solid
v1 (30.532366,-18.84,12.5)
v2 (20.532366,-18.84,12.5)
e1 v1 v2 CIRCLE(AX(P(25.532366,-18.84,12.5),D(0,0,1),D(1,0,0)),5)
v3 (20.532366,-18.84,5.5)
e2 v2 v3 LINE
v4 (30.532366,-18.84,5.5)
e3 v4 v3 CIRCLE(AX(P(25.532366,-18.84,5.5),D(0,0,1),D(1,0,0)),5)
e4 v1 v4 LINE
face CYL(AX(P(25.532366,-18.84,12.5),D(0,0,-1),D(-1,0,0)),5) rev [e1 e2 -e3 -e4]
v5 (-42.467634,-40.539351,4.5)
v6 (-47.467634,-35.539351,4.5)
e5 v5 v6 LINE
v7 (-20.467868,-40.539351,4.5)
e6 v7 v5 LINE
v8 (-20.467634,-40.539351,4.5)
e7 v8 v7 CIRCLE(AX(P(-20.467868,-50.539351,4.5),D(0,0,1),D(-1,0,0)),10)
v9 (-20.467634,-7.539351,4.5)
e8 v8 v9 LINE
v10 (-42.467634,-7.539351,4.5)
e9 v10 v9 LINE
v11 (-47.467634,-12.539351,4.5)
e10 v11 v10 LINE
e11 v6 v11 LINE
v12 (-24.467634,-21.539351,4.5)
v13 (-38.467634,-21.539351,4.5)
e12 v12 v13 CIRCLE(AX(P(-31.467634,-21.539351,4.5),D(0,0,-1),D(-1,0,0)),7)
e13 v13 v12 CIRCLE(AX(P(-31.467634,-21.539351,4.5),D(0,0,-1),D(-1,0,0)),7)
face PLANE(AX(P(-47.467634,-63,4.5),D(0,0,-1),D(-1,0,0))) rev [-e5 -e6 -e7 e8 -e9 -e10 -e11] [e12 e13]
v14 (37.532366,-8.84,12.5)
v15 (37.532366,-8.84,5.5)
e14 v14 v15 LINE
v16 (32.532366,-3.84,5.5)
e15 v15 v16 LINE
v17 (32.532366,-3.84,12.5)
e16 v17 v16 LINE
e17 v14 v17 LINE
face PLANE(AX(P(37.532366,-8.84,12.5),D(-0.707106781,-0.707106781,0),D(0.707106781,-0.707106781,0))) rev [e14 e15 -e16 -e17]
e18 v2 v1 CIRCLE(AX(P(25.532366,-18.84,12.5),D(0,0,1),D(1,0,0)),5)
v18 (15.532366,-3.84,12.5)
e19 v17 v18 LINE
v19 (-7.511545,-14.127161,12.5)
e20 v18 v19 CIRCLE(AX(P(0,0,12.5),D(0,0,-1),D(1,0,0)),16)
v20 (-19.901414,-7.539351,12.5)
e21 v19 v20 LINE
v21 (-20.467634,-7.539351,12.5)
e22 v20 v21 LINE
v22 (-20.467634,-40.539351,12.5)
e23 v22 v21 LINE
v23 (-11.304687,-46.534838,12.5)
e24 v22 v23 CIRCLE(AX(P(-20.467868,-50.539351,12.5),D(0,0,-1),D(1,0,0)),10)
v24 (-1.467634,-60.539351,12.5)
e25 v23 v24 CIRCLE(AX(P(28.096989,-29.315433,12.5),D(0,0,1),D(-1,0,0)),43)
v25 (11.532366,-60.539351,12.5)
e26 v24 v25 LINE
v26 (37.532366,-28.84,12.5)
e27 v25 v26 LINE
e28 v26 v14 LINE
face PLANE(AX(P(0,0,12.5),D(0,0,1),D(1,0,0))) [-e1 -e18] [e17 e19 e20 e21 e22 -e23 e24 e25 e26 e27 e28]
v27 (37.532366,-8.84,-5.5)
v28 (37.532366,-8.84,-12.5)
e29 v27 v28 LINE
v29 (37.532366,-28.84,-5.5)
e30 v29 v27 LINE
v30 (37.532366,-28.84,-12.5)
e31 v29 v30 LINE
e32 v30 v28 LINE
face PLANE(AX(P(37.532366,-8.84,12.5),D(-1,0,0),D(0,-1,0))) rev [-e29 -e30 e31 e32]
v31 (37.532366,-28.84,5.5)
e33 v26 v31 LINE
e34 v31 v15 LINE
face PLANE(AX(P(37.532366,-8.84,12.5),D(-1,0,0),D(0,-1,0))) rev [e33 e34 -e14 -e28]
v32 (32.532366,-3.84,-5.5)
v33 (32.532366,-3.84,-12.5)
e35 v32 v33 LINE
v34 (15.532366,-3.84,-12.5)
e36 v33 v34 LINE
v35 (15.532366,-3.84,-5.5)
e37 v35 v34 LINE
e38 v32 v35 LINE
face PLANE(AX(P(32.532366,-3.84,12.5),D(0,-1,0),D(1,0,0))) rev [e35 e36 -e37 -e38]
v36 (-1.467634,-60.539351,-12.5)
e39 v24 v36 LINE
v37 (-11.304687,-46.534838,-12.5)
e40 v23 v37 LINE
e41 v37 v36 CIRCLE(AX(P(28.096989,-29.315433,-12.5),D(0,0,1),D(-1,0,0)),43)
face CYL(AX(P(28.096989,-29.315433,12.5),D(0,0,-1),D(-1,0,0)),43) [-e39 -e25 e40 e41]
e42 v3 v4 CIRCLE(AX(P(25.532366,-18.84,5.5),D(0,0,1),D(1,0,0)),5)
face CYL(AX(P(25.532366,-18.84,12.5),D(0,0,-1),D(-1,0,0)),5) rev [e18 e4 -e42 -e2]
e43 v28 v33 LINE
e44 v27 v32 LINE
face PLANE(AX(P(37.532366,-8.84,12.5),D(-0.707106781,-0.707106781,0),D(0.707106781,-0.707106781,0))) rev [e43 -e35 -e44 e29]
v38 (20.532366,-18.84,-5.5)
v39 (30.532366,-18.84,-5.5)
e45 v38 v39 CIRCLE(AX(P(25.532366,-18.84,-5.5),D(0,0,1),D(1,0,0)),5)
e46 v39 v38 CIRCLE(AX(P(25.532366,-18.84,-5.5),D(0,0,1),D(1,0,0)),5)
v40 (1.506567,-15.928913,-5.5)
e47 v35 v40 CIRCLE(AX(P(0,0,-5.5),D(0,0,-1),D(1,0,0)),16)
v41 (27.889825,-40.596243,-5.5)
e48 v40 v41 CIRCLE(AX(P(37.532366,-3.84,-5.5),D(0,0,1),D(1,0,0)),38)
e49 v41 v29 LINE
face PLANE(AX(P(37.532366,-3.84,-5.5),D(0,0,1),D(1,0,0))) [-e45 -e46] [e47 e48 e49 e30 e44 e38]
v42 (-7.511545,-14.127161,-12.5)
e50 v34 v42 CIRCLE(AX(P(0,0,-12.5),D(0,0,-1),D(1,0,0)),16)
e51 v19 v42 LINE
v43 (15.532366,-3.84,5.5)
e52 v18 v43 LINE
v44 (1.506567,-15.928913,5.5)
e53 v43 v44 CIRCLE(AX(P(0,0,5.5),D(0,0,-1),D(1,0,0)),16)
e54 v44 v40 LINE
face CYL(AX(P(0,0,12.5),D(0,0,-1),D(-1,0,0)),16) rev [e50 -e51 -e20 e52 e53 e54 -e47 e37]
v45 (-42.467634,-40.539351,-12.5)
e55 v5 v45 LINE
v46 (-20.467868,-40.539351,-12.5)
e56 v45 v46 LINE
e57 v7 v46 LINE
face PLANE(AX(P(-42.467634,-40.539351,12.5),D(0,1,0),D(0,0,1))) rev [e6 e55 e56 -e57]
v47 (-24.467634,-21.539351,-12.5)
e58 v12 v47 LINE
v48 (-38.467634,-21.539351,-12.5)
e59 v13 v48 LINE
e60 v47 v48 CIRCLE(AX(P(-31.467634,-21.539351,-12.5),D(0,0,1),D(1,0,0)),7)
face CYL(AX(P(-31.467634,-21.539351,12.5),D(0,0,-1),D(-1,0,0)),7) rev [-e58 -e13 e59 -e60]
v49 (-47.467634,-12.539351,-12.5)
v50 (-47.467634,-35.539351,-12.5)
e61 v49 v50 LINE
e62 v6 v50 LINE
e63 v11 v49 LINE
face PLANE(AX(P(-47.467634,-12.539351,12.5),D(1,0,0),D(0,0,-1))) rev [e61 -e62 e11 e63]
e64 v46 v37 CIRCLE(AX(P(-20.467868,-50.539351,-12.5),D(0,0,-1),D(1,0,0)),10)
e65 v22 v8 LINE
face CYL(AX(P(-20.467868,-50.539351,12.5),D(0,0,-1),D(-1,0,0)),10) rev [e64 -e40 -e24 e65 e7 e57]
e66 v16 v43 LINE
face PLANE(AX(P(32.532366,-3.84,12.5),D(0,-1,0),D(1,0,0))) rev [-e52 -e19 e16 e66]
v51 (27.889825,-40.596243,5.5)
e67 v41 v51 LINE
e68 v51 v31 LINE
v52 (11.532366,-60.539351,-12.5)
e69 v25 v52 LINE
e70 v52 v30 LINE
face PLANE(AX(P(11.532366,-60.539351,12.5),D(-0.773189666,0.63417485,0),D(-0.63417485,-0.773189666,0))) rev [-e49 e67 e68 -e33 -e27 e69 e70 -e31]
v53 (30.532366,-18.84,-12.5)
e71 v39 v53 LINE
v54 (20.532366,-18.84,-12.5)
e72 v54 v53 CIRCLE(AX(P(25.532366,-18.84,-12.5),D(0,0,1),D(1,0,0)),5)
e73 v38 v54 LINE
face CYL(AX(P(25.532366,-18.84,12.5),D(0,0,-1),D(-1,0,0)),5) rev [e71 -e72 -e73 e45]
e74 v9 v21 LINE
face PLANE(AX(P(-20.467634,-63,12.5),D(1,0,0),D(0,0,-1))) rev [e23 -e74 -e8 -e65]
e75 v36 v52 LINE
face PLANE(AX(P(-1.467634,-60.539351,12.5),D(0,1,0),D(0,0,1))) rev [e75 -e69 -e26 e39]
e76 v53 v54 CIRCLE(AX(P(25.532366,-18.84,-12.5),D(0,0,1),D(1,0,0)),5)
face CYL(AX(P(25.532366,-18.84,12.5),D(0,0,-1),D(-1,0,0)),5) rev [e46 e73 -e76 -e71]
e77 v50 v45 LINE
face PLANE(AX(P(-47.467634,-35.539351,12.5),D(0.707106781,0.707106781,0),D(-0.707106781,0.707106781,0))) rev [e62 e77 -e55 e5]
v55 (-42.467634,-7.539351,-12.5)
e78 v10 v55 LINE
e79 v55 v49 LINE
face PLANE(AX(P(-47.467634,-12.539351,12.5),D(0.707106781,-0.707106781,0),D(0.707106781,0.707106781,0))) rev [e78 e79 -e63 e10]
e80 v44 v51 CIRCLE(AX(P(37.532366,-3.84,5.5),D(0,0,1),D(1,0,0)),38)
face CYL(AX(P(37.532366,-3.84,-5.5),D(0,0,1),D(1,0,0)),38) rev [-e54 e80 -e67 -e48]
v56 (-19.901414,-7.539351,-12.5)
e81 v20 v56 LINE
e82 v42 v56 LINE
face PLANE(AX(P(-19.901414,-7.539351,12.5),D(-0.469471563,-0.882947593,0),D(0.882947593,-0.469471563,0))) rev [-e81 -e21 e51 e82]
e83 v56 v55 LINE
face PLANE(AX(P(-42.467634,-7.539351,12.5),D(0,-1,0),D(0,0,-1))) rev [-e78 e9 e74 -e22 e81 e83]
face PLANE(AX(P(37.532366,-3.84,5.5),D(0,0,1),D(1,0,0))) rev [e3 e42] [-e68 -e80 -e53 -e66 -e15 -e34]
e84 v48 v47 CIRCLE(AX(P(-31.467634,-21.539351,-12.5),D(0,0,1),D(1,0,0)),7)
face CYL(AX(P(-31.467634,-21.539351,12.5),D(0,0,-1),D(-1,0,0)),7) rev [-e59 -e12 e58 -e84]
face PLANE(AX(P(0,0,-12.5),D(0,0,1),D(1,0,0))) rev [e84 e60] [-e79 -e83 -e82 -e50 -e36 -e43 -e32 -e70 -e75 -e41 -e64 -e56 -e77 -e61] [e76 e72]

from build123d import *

# Parameters (mm, degrees)
BRACKET_PROFILE_SKETCH_R   = 5
BRACKET_PROFILE_SKETCH_R_2 = 7
BRACKET_BODY_25MM_DEPTH    = 12.5
FORK_SLOT_SKETCH_W         = 27
FORK_SLOT_SKETCH_H         = 8
FORK_SLOT_8X27_DEPTH       = 63
RELIEF_CIRCLE_SKETCH_76_R  = 38
FRONT_RELIEF_CUT_76_DEPTH  = 5.5


with BuildPart() as part:
    # Bracket Profile Sketch → Bracket Body 25mm (new, symmetric)
    with BuildSketch(Plane.XY):
        with BuildLine():
            Line((-1.467633793, -60.539351202), (11.532366207, -60.539351202))
            Line((11.532366207, -60.539351202), (37.532366207, -28.84))
            Line((37.532366207, -28.84), (37.532366207, -8.84))
            Line((37.532366207, -8.84), (32.532366207, -3.84))
            Line((32.532366207, -3.84), (15.532366207, -3.84))
            ThreePointArc((15.532366207, -3.84), (6.522255442, -14.610276655), (-7.511545005, -14.127161486))
            Line((-7.511545005, -14.127161486), (-19.901414154, -7.539351202))
            Line((-19.901414154, -7.539351202), (-42.467633793, -7.539351202))
            Line((-42.467633793, -7.539351202), (-47.467633793, -12.539351202))
            Line((-47.467633793, -12.539351202), (-47.467633793, -35.539351202))
            Line((-47.467633793, -35.539351202), (-42.467633793, -40.539351202))
            Line((-42.467633793, -40.539351202), (-20.467867574, -40.539351202))
            ThreePointArc((-20.467867574, -40.539351202), (-14.992702243, -42.171402553), (-11.304687106, -46.534838282))
            ThreePointArc((-11.304687106, -46.534838282), (-7.089928905, -54.031435949), (-1.467633793, -60.539351202))
        make_face()
        with Locations((25.532366207, -18.84)):
            Circle(BRACKET_PROFILE_SKETCH_R, mode=Mode.SUBTRACT)
        with Locations((-31.467633793, -21.539351202)):
            Circle(BRACKET_PROFILE_SKETCH_R_2, mode=Mode.SUBTRACT)
    extrude(amount=BRACKET_BODY_25MM_DEPTH, both=True)

    # Fork Slot Sketch → Fork Slot 8x27 (cut)
    with BuildSketch(Plane(origin=(0, 0, 0), x_dir=(1, 0, 0), z_dir=(0, 1, 0))):
        with Locations((-33.967633793, -8.5)):
            Rectangle(FORK_SLOT_SKETCH_W, FORK_SLOT_SKETCH_H)
    extrude(amount=-FORK_SLOT_8X27_DEPTH, mode=Mode.SUBTRACT)

    # Relief Circle Sketch Ø76 → Front Relief Cut Ø76 (cut, symmetric)
    with BuildSketch(Plane.XY):
        with Locations((37.532366207, -3.84)):
            Circle(RELIEF_CIRCLE_SKETCH_76_R)
    extrude(amount=FRONT_RELIEF_CUT_76_DEPTH, both=True, mode=Mode.SUBTRACT)


solid = part.part
